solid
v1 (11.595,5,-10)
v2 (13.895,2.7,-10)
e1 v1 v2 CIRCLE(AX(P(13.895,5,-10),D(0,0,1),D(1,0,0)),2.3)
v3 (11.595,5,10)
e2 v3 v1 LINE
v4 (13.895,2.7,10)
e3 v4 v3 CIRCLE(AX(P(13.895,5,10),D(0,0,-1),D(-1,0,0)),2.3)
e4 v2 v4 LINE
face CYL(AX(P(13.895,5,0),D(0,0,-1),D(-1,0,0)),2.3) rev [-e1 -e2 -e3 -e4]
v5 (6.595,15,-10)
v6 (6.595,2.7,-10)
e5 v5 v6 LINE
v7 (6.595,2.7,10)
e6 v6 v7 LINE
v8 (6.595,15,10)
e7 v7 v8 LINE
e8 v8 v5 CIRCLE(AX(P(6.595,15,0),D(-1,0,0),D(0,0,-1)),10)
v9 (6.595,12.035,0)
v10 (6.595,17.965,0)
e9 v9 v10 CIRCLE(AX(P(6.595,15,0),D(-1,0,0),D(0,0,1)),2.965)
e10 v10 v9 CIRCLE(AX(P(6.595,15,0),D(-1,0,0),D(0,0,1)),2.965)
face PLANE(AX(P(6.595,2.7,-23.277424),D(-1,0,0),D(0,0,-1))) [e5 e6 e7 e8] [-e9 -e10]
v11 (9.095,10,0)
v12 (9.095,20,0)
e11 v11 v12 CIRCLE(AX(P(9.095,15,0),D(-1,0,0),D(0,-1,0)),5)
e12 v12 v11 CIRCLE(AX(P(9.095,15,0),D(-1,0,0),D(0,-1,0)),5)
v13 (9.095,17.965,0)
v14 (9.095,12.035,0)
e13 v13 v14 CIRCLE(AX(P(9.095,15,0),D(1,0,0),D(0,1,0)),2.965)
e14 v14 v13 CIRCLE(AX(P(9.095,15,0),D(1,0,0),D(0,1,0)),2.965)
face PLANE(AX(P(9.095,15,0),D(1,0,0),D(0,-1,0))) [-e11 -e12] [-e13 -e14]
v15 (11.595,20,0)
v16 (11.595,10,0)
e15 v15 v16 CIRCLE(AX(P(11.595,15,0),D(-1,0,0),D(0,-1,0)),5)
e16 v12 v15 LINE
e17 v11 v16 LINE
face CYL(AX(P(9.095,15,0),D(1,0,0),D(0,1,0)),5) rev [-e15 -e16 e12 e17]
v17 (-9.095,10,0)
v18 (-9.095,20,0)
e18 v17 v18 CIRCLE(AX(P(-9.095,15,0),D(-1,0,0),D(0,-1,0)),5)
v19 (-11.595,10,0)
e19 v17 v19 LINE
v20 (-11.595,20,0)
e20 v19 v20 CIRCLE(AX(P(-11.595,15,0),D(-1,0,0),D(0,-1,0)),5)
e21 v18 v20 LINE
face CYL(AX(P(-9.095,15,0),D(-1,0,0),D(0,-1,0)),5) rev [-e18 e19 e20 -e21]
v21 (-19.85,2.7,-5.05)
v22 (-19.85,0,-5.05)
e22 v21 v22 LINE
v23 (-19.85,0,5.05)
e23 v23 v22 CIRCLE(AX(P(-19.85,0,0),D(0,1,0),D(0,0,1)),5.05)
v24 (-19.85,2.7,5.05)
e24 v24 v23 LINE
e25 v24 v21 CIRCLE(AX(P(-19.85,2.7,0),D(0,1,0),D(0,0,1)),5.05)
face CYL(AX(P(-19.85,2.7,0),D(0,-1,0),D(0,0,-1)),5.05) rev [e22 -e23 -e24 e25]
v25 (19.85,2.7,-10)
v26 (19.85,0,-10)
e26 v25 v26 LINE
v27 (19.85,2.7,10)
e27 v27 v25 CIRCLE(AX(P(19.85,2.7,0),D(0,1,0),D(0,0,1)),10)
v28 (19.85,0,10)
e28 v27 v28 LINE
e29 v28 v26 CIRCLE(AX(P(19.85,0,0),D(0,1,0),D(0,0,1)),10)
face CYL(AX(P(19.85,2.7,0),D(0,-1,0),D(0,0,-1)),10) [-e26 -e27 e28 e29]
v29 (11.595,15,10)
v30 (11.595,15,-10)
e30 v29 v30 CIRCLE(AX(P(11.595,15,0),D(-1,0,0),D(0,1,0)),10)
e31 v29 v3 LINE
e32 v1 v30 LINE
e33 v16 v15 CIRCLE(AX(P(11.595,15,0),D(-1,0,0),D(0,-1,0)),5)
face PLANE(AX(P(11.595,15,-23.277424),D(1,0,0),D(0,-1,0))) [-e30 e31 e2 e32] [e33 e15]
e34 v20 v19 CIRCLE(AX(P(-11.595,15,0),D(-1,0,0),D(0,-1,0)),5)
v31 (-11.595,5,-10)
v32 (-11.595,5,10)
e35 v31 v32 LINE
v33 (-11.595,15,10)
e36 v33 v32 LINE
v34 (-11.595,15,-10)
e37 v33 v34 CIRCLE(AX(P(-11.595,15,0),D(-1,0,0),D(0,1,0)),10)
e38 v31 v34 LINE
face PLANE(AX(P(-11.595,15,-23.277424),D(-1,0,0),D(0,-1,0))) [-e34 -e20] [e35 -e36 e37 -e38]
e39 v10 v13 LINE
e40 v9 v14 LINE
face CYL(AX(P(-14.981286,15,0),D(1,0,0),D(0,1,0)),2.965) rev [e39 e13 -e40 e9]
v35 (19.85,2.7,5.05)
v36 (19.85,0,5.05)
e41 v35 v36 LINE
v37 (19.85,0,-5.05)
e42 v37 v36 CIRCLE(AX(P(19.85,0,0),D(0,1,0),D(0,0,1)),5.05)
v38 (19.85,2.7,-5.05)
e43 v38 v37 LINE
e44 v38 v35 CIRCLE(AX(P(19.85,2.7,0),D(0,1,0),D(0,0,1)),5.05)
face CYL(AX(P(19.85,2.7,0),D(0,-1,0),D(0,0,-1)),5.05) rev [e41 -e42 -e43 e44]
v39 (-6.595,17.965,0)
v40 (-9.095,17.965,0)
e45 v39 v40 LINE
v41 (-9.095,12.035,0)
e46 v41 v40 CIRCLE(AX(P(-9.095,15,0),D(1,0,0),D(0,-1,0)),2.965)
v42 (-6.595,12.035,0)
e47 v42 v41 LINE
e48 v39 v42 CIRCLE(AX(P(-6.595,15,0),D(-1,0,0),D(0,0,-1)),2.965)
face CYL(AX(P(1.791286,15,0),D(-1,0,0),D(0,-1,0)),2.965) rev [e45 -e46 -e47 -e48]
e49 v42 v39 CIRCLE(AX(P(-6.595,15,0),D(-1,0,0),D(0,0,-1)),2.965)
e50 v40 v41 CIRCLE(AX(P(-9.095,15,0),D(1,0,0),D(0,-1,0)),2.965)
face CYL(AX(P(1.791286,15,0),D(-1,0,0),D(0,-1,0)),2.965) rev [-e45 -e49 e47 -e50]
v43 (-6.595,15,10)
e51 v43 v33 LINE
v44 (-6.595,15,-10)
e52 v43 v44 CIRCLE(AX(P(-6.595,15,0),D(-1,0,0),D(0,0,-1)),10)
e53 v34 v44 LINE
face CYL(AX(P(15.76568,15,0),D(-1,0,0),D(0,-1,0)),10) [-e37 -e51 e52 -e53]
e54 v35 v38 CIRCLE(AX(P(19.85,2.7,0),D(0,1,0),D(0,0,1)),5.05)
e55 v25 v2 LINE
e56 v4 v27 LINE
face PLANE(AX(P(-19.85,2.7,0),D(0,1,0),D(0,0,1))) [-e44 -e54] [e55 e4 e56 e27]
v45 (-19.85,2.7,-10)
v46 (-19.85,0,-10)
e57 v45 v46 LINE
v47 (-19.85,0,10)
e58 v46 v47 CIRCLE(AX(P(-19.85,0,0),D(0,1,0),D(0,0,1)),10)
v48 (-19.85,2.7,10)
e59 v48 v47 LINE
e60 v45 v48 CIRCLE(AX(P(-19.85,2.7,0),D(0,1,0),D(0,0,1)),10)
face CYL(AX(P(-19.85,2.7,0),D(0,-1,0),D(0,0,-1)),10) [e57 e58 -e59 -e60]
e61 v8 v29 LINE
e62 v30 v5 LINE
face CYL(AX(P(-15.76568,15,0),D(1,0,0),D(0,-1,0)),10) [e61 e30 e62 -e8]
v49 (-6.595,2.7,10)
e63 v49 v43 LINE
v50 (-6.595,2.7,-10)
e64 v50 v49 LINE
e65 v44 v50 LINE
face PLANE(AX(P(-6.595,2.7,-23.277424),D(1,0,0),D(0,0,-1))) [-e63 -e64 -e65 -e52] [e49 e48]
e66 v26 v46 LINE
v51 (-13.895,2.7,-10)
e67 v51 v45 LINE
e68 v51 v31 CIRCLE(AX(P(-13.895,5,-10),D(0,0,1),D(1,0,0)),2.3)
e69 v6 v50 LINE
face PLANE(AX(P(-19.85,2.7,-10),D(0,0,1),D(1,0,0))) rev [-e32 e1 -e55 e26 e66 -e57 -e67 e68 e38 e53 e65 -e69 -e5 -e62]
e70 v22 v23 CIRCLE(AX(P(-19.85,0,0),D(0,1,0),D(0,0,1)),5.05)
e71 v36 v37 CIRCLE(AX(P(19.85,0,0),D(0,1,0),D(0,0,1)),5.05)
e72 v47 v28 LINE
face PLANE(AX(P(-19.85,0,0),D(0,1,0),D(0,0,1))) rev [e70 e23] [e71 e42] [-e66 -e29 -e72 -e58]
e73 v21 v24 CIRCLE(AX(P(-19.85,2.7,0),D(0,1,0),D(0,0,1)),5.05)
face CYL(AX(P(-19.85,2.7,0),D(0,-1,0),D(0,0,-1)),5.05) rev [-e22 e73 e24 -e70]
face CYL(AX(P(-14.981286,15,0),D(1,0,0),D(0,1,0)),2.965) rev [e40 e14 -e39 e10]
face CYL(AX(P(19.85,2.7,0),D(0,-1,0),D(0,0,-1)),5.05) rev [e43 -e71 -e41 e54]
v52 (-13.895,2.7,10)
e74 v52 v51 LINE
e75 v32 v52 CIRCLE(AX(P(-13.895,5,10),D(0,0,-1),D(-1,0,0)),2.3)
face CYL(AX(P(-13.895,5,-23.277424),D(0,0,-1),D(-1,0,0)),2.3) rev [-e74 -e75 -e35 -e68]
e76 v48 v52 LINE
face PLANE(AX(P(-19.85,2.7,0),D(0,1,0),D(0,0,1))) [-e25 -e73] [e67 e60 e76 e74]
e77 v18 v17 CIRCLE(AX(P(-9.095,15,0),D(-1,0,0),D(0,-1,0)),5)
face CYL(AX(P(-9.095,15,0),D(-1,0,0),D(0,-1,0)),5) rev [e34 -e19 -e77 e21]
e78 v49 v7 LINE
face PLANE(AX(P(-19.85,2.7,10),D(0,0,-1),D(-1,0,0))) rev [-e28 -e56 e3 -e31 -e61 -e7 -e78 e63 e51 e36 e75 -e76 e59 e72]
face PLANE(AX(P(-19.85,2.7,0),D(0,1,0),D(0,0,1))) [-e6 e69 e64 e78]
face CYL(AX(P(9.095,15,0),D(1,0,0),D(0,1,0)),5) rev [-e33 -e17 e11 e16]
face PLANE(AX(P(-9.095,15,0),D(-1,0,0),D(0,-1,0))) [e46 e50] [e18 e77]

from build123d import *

# Parameters (mm, degrees)
BASE_PLATE_SKETCH_R      = 5.05
BASE_PLATE_DEPTH         = 2.7
LUG_SKETCH_W             = 5
LUG_SKETCH_H             = 12.3
LUG_DEPTH                = 20
LUG_WEB_DEPTH            = 5
FILLET_R2_3_R            = 2.3
PIN_HOLE_SKETCH_R        = 2.965
PIN_HOLE_5_93_DEPTH      = 5
COUNTERBORE_SKETCH_R     = 5
COUNTERBORE_10X2_5_DEPTH = 2.5


with BuildPart() as part:
    # Base Plate Sketch → Base Plate (new body)
    with BuildSketch(Plane(origin=(0, 0, 0), x_dir=(1, 0, 0), z_dir=(0, 1, 0))):
        with BuildLine():
            Line((-19.85, 10), (19.85, 10))
            ThreePointArc((19.85, 10), (29.85, 0), (19.85, -10))
            Line((19.85, -10), (-19.85, -10))
            ThreePointArc((-19.85, -10), (-29.85, 0), (-19.85, 10))
        make_face()
        with Locations(Location((-19.85, 0, 0), (0, 0, 90))):
            Circle(BASE_PLATE_SKETCH_R, mode=Mode.SUBTRACT)
        with Locations(Location((19.85, 0, 0), (0, 0, 90))):
            Circle(BASE_PLATE_SKETCH_R, mode=Mode.SUBTRACT)
    extrude(amount=BASE_PLATE_DEPTH)

    # Lug Sketch → Lug (add)
    with BuildSketch(Plane.XY.offset(10)):
        with Locations((-9.095, 8.85)):
            Rectangle(LUG_SKETCH_W, LUG_SKETCH_H)
    extrude(amount=-LUG_DEPTH)

    # Lug Web Sketch → Lug Web (add)
    with BuildSketch(Plane.ZY.offset(11.595)):
        with BuildLine():
            Line((-10, 15), (10, 15))
            ThreePointArc((10, 15), (0, 25), (-10, 15))
        make_face()
    extrude(amount=-LUG_WEB_DEPTH)

    # Base Plate Mirror: part across plane


with BuildPart() as part_1:
    add(part.part)
    add(part.part.mirror(Plane(origin=(0, 0, 0), x_dir=(0, 0, 1), z_dir=(1, 0, 0))))

    # Fillet R2.3
    fillet_r2_3_edges = [part_1.edges().sort_by_distance(p)[0] for p in [
        (-11.595, 2.7, 0),
        (11.595, 2.7, 0),
    ]]
    fillet(fillet_r2_3_edges, radius=FILLET_R2_3_R)

    # Pin Hole Sketch → Pin Hole Ø5.93 (cut)
    with BuildSketch(Plane.ZY.offset(11.595)):
        with Locations(Location((0, 15, 0), (0, 0, 270))):
            Circle(PIN_HOLE_SKETCH_R)
    pin_hole_5_93 = extrude(amount=-PIN_HOLE_5_93_DEPTH, mode=Mode.SUBTRACT)

    # Counterbore Sketch → Counterbore Ø10x2.5 (cut)
    with BuildSketch(Plane.ZY.offset(11.595)):
        with Locations(Location((0, 15, 0), (0, 0, 270))):
            Circle(COUNTERBORE_SKETCH_R)
    counterbore_10x2_5 = extrude(amount=-COUNTERBORE_10X2_5_DEPTH, mode=Mode.SUBTRACT)

    # Pin Hole Mirror: Pin Hole Ø5.93, Counterbore Ø10x2.5 across plane
    add(pin_hole_5_93.mirror(Plane(origin=(0, 0, 0), x_dir=(0, 0, 1), z_dir=(1, 0, 0))), mode=Mode.SUBTRACT)
    add(counterbore_10x2_5.mirror(Plane(origin=(0, 0, 0), x_dir=(0, 0, 1), z_dir=(1, 0, 0))), mode=Mode.SUBTRACT)


solid = part_1.part
